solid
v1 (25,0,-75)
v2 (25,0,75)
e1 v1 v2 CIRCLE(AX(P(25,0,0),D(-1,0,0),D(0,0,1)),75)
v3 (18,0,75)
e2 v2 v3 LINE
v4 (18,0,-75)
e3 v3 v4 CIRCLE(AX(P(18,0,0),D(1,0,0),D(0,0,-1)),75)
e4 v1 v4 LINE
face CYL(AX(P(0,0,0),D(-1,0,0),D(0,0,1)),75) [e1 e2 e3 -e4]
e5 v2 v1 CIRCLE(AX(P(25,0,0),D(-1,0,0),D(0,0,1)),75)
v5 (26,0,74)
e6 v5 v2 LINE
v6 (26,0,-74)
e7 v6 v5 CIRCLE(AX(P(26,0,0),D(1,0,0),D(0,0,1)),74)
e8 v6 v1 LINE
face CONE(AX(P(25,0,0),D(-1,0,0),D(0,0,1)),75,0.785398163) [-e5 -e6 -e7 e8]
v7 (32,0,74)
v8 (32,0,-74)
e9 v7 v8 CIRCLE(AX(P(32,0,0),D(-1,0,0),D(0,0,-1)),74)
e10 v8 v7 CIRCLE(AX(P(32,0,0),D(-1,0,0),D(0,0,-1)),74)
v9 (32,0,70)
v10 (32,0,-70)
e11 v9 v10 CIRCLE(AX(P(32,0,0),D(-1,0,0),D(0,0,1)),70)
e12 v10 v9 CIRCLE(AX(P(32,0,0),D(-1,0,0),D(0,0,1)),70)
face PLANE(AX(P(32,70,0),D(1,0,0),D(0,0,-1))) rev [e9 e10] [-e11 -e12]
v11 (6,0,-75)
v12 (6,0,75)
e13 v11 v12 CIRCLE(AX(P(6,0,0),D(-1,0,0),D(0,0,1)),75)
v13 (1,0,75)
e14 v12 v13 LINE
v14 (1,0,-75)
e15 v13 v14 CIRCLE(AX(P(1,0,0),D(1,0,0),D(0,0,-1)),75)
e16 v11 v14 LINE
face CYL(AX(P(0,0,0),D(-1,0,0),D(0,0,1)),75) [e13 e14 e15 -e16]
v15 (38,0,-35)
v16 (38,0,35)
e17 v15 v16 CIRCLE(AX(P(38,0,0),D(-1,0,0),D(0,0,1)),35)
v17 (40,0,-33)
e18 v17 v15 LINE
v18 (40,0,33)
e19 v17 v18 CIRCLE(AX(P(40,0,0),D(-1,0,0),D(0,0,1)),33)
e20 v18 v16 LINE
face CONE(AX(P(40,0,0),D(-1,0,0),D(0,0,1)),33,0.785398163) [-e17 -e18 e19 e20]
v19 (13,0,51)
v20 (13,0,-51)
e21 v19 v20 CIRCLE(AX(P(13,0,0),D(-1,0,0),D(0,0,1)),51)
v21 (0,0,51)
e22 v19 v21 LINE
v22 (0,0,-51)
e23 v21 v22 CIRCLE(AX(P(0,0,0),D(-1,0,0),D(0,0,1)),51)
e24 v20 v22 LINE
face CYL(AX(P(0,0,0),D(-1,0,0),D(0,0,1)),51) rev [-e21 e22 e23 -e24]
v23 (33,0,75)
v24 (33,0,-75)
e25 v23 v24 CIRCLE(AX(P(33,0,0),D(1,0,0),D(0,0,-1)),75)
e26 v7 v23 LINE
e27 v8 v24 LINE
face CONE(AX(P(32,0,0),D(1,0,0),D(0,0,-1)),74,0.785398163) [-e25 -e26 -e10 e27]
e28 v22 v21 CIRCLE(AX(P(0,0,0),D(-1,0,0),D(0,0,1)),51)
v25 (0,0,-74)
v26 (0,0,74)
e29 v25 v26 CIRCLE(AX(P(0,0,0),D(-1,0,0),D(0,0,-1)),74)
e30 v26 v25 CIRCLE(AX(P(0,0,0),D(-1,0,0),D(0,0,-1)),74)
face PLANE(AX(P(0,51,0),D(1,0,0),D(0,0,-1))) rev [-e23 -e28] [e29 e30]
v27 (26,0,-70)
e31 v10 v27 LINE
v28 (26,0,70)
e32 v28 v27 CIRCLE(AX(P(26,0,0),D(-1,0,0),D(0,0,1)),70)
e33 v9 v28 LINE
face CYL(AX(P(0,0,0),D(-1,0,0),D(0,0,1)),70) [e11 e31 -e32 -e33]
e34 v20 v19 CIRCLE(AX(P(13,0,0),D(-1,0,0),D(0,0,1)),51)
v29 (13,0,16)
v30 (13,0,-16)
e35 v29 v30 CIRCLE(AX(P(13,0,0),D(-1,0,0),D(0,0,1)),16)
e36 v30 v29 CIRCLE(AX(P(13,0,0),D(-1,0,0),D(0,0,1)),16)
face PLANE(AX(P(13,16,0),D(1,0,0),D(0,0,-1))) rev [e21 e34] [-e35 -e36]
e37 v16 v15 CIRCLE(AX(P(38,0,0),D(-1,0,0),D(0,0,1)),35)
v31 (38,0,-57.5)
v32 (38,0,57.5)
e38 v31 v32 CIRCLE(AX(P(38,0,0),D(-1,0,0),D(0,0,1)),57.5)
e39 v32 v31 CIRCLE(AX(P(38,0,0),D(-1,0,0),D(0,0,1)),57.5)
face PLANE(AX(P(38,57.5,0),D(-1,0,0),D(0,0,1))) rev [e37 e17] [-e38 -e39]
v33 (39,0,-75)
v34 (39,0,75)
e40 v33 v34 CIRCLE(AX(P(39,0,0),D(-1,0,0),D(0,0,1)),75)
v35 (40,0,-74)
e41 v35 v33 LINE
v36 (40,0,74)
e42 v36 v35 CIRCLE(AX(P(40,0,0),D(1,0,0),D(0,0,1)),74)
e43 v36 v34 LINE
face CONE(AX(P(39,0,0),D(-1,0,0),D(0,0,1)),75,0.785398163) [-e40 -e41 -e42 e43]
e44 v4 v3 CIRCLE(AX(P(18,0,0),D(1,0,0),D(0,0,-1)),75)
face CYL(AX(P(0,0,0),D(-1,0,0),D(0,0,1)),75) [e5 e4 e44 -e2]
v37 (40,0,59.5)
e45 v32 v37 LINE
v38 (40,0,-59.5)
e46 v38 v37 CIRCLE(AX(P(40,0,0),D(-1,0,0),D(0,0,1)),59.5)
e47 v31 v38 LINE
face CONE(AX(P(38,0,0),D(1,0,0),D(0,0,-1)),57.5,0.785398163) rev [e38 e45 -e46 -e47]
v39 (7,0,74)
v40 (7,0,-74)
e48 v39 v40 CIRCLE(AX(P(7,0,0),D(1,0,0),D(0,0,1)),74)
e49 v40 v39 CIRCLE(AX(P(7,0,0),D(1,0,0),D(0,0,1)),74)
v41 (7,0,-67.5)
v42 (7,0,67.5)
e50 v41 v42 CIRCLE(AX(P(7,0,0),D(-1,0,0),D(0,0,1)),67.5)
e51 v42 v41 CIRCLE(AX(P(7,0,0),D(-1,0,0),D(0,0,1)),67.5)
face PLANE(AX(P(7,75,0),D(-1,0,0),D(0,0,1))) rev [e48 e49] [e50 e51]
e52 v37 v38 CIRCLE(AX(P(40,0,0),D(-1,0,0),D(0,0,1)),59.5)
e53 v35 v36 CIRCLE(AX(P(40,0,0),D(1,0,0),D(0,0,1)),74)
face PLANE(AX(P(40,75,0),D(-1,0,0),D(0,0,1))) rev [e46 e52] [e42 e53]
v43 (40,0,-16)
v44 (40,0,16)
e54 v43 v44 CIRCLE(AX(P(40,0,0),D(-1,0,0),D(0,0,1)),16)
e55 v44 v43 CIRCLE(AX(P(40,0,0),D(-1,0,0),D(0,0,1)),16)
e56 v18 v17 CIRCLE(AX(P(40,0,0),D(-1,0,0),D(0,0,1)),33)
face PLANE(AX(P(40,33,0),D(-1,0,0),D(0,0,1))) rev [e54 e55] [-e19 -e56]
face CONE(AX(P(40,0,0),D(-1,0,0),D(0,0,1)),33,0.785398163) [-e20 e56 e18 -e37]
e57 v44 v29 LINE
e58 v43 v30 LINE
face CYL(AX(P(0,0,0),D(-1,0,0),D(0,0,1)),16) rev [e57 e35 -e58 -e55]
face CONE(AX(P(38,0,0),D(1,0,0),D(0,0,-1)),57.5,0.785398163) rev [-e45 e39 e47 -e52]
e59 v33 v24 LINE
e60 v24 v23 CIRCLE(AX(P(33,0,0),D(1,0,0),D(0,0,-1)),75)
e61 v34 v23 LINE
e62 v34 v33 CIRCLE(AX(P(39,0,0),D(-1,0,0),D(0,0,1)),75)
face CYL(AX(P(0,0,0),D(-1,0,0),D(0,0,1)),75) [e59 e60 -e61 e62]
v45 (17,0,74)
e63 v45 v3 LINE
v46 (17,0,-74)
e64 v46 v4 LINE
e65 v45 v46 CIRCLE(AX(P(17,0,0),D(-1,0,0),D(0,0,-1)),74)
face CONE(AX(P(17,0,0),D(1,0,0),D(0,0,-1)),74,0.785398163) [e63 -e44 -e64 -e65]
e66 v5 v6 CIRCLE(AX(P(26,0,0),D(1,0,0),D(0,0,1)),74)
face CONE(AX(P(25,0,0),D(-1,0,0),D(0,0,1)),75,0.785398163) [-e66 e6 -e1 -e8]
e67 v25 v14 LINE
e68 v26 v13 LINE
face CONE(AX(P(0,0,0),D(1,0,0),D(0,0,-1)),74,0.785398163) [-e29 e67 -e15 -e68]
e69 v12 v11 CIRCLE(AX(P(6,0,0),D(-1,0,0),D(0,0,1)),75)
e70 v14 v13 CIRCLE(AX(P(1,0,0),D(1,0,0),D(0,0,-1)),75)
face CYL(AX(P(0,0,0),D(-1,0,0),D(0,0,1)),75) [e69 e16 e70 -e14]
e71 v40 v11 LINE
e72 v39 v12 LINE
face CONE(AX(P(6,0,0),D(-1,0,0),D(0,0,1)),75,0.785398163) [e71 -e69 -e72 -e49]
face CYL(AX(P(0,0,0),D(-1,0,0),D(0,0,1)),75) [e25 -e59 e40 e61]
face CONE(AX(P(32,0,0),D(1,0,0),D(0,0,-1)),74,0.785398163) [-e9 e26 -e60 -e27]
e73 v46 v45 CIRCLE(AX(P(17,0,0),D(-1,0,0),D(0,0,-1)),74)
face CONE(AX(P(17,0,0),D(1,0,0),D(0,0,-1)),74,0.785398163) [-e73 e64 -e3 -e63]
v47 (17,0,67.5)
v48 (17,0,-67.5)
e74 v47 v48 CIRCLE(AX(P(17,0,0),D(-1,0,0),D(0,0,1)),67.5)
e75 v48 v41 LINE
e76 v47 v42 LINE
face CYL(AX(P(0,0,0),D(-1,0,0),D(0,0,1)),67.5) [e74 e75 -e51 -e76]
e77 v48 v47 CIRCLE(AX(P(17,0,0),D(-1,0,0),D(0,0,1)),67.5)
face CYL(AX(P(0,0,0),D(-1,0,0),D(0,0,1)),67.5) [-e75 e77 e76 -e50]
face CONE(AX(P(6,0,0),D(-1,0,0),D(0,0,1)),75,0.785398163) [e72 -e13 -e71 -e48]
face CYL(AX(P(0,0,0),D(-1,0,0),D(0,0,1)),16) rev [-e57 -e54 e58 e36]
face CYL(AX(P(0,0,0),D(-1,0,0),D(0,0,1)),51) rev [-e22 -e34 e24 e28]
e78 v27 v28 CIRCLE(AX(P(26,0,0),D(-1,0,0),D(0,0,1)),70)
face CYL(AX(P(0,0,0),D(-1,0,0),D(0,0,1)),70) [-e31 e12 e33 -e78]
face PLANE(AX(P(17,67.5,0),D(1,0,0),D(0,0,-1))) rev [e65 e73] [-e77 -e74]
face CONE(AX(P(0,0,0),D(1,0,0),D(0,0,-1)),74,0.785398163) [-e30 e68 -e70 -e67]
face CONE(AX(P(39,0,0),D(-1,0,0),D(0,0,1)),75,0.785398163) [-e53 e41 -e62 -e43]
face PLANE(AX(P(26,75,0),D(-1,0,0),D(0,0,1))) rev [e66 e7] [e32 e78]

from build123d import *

# Parameters (mm, degrees)
CHAMFER_1_SIZE = 1


with BuildPart() as part:
    # 草图1 → 旋转1 (revolve)
    with BuildSketch(Plane.XY, mode=Mode.PRIVATE) as revolve_1_sk:
        Polygon((0, 51), (0, 75), (7, 75), (7, 67.5), (17, 67.5), (17, 75), (26, 75), (26, 70), (32, 70), (32, 75), (40, 75), (40, 59.5), (38, 57.5), (38, 35), (40, 33), (40, 16), (13, 16), (13, 51), align=None)
    revolve(revolve_1_sk.sketch.rotate(Axis((0, 0, 0), (1, 0, 0)), 90), axis=Axis((0, 0, 0), (1, 0, 0)))

    # 倒角1
    chamfer_1_edges = [part.edges().sort_by_distance(p)[0] for p in [
        (40, 0, -75),
        (32, 0, -75),
        (26, 0, -75),
        (17, 0, -75),
        (7, 0, -75),
        (0, 0, -75),
    ]]
    chamfer(chamfer_1_edges, length=CHAMFER_1_SIZE)


solid = part.part
